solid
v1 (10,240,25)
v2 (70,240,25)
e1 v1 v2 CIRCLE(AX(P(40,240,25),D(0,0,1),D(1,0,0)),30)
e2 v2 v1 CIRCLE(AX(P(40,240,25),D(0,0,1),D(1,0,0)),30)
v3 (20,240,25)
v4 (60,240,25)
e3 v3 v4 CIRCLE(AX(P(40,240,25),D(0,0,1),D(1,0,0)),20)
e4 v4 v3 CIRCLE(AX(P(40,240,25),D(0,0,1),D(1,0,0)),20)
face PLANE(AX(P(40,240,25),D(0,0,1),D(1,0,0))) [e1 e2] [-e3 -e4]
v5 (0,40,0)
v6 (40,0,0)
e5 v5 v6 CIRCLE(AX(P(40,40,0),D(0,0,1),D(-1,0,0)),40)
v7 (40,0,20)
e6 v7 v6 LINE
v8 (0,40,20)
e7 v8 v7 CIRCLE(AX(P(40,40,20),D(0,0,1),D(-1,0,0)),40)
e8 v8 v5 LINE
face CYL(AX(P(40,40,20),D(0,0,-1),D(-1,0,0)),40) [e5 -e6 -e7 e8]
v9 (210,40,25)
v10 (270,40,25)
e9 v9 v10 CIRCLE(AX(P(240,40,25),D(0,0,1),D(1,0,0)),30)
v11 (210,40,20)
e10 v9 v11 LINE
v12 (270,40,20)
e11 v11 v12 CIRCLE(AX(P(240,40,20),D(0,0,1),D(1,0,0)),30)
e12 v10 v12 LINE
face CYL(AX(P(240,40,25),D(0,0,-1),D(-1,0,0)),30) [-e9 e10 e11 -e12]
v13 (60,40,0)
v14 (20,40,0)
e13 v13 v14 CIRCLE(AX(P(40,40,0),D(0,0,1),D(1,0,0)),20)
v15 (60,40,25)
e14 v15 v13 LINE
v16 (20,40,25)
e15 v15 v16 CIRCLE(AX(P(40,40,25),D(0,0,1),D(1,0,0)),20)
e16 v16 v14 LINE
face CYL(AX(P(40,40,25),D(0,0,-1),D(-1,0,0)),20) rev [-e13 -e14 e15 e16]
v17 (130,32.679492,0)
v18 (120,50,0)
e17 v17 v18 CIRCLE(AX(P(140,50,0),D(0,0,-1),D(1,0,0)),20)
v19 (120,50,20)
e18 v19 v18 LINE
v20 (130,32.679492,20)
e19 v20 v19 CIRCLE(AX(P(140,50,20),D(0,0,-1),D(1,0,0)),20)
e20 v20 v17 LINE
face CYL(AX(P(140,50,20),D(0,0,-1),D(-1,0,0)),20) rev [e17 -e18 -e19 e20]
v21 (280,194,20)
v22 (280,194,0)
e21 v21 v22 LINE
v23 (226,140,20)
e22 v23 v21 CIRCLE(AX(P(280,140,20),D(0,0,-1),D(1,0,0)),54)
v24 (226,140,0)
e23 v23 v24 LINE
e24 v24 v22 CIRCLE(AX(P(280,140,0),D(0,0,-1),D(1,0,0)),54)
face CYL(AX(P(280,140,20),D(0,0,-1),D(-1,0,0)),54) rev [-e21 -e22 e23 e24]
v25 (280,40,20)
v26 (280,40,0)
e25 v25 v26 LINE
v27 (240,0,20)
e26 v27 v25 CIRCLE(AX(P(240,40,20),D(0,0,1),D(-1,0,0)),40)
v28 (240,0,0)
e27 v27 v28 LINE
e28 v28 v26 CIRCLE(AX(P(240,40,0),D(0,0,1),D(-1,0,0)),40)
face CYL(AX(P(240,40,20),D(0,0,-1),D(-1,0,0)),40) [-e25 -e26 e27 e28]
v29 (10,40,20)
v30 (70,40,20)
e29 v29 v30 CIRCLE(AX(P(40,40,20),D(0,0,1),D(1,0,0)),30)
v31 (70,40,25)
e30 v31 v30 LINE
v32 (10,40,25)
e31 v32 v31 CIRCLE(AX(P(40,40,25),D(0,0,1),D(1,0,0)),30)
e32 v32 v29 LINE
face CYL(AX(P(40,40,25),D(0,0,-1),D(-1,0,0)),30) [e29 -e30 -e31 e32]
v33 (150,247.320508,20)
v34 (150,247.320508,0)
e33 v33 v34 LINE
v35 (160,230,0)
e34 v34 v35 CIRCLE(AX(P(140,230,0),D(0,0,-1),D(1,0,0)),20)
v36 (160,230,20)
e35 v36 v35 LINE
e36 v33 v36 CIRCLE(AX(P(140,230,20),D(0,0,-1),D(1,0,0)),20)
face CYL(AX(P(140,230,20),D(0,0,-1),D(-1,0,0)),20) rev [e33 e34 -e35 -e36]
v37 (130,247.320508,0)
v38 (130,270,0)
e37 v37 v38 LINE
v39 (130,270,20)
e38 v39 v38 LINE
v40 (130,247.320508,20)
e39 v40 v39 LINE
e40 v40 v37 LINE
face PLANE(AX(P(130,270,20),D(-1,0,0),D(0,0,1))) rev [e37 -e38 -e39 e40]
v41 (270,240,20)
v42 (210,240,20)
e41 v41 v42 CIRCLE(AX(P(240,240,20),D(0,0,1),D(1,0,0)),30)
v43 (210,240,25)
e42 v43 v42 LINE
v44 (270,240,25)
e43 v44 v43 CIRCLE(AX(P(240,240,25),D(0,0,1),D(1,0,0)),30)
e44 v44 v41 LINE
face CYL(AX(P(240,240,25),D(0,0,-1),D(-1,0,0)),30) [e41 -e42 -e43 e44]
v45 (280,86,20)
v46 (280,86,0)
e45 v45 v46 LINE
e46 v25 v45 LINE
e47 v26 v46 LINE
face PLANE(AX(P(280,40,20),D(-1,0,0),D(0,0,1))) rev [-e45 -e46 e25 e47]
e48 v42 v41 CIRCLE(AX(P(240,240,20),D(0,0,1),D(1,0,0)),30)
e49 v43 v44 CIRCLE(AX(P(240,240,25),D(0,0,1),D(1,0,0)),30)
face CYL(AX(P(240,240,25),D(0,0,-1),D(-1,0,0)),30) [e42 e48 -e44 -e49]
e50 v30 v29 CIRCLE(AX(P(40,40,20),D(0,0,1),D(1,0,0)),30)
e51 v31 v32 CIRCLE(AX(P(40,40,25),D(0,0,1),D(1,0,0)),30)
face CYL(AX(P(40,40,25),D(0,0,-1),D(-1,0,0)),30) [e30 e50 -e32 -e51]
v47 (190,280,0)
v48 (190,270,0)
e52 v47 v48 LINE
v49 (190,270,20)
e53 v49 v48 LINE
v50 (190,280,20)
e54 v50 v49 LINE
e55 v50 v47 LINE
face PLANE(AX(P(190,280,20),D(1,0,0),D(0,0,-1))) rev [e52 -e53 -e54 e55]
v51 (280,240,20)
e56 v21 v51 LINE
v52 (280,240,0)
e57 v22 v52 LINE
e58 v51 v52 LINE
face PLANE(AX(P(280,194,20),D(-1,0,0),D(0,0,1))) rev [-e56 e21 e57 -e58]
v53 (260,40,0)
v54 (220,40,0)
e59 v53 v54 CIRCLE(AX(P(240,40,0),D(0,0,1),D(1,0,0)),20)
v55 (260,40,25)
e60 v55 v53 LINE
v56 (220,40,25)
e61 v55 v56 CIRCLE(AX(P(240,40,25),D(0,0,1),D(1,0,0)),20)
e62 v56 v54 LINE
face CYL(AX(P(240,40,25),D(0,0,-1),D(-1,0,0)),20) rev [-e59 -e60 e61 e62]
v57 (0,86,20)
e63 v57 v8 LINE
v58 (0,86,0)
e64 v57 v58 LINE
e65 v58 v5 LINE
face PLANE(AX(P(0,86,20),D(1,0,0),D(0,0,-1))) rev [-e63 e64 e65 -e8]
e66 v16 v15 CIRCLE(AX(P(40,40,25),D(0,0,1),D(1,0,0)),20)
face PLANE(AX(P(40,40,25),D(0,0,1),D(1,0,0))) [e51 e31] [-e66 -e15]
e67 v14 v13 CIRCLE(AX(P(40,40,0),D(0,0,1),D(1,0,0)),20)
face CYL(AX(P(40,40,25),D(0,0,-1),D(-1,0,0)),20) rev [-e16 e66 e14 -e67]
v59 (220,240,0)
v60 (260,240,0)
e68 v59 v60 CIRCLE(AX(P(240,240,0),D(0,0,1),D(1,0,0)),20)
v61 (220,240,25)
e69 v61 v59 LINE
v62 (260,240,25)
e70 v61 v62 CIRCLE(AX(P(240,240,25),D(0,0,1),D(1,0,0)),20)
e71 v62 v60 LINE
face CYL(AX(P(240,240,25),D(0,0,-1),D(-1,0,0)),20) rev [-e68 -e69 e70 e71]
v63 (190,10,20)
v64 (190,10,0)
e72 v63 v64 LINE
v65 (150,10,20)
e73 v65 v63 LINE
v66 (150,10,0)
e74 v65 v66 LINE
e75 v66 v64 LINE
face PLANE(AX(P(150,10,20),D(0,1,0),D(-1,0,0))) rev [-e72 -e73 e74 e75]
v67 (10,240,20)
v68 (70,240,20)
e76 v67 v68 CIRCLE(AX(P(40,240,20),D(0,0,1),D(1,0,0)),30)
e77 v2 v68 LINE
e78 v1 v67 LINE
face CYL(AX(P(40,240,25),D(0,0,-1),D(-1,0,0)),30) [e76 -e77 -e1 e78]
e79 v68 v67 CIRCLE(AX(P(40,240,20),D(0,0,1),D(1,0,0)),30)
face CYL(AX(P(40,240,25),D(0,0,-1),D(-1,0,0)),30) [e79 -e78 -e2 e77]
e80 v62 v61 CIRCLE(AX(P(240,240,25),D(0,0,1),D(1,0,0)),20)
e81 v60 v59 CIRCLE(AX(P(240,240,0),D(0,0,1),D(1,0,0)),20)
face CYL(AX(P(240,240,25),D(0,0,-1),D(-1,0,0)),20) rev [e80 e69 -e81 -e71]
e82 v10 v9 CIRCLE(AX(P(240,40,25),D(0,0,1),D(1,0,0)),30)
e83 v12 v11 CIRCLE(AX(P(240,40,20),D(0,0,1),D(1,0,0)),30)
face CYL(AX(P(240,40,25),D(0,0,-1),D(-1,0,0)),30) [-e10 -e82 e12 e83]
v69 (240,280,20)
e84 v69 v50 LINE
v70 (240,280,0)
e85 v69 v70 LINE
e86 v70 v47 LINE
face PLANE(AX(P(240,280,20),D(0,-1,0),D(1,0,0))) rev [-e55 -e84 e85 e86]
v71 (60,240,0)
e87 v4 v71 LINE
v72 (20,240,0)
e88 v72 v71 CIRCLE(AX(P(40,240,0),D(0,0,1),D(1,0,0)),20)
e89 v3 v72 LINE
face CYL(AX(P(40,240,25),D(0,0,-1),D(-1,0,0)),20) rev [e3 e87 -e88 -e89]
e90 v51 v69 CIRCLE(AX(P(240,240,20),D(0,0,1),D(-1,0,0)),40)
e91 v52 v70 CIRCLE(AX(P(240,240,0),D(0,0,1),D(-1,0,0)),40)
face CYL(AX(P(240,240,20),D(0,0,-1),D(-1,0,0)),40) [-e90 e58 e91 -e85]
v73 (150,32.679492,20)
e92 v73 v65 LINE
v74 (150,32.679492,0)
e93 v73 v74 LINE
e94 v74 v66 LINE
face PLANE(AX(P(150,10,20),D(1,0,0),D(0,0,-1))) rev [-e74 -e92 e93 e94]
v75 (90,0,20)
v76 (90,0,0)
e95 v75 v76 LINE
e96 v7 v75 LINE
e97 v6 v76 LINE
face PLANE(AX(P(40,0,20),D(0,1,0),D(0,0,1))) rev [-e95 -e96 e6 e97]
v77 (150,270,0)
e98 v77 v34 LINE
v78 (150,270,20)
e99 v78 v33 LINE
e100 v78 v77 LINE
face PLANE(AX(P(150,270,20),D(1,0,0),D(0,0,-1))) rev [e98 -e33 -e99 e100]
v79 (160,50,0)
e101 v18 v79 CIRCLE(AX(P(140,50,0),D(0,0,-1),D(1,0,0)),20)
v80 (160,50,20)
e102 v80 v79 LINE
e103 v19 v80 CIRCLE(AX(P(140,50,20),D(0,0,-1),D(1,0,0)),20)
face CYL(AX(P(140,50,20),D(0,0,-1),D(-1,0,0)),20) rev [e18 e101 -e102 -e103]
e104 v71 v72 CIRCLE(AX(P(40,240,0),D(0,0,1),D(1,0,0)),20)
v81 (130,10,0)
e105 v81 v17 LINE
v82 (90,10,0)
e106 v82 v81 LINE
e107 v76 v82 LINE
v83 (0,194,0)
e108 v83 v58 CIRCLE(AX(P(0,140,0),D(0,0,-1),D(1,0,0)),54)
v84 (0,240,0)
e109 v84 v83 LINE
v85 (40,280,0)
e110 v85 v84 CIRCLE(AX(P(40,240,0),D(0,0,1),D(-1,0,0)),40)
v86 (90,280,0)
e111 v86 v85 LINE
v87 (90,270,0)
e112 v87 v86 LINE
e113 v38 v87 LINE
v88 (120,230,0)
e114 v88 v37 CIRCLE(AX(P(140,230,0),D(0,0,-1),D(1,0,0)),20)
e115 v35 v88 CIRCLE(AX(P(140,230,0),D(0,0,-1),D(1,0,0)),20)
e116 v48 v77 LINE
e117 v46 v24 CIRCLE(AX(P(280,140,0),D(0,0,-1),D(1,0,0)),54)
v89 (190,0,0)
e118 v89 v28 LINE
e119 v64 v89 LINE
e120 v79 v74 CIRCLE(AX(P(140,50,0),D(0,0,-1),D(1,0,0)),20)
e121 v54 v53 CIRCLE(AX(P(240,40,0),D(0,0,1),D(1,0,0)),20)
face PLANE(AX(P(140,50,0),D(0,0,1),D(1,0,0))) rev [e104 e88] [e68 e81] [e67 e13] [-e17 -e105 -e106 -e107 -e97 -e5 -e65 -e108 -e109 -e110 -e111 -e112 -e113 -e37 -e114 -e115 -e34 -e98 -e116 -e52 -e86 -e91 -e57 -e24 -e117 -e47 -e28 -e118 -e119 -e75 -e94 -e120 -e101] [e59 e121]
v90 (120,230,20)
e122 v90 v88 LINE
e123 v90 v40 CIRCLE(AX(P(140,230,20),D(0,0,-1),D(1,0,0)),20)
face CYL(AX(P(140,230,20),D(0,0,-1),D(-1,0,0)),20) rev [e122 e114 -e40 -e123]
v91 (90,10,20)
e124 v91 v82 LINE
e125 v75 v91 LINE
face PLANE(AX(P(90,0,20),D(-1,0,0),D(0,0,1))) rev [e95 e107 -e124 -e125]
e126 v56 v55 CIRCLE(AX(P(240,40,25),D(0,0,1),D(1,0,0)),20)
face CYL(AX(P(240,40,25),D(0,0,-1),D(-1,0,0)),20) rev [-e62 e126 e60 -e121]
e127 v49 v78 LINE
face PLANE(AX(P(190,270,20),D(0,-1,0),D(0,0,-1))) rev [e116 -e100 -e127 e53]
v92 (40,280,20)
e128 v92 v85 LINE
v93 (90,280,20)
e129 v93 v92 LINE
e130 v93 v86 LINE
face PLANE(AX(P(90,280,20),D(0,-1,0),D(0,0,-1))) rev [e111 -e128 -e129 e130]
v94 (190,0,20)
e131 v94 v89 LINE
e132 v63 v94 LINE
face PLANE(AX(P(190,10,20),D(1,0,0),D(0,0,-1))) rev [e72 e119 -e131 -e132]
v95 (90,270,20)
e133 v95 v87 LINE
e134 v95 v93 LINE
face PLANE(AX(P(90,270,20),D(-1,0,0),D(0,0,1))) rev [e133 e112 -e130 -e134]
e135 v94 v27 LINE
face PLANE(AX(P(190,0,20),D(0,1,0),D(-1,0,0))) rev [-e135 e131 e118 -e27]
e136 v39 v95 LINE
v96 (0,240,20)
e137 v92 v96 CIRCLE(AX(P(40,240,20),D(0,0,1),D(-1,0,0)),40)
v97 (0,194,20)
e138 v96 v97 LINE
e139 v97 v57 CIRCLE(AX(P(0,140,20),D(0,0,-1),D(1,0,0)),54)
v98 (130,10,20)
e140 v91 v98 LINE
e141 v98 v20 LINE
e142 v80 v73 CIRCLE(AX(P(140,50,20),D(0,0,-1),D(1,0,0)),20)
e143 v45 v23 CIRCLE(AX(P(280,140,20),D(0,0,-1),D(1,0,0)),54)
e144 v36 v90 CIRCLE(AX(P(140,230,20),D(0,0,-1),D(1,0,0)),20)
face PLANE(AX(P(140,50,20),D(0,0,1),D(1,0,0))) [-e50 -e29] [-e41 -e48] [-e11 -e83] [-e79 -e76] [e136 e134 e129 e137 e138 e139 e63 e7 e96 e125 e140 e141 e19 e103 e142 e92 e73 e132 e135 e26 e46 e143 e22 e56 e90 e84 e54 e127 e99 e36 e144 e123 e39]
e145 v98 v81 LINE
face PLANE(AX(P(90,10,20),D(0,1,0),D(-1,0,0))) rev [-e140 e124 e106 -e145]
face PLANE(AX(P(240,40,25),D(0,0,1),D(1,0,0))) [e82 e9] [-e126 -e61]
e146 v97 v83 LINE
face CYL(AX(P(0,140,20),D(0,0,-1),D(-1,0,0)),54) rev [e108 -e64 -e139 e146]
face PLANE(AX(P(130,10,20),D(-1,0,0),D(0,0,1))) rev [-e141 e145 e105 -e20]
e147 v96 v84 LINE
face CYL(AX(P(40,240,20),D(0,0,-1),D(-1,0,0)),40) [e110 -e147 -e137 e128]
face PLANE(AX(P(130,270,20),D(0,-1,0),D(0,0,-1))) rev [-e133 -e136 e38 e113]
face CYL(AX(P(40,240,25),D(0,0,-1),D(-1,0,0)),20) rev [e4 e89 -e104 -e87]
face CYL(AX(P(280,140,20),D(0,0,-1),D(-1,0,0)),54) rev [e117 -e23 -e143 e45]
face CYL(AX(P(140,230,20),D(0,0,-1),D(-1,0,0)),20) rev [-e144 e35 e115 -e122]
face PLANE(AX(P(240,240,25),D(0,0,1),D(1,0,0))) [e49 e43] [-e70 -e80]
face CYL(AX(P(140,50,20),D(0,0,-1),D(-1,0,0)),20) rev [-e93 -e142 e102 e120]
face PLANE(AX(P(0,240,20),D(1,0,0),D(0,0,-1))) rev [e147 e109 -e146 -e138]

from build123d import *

# Parameters (mm, degrees)
BASE_PLATE_20MM_DEPTH          = 20
MOUNTING_BOSS_RINGS_SKETCH_R   = 30
MOUNTING_BOSS_RINGS_SKETCH_R_2 = 20
MOUNTING_BOSSES_4X_60_DEPTH    = 5
TOP_NOTCH_SKETCH_R             = 20
TOP_NOTCH_CUT_DEPTH            = 397.484552032


with BuildPart() as part:
    # Plate Profile Sketch → Base Plate 20mm (new body)
    with BuildSketch(Plane.XY):
        with BuildLine():
            Line((40, 0), (90, 0))
            Line((90, 0), (90, 10))
            Line((90, 10), (130, 10))
            Line((130, 10), (130, 32.679491924))
            ThreePointArc((130, 32.679491924), (140, 70), (150, 32.679491924))
            Line((150, 32.679491924), (150, 10))
            Line((150, 10), (190, 10))
            Line((190, 10), (190, 0))
            Line((190, 0), (240, 0))
            ThreePointArc((240, 0), (268.284271247, 11.715728753), (280, 40))
            Line((280, 40), (280, 86))
            ThreePointArc((280, 86), (226, 140), (280, 194))
            Line((280, 194), (280, 240))
            ThreePointArc((280, 240), (268.284271247, 268.284271247), (240, 280))
            Line((240, 280), (190, 280))
            Line((190, 280), (190, 270))
            Line((190, 270), (150, 270))
            Line((150, 270), (150, 247.320508076))
            ThreePointArc((150, 247.320508076), (140, 210), (130, 247.320508076))
            Line((130, 247.320508076), (130, 270))
            Line((130, 270), (90, 270))
            Line((90, 270), (90, 280))
            Line((90, 280), (40, 280))
            ThreePointArc((40, 280), (11.715728753, 268.284271247), (0, 240))
            Line((0, 240), (0, 194))
            ThreePointArc((0, 194), (54, 140), (0, 86))
            Line((0, 86), (0, 40))
            ThreePointArc((0, 40), (11.715728753, 11.715728753), (40, 0))
        make_face()
    extrude(amount=BASE_PLATE_20MM_DEPTH)

    # Mounting Boss Rings Sketch → Mounting Bosses 4xØ60 (add)
    # profile 1 of 4: a face of its own
    with BuildSketch(Plane.XY.offset(20)):
        with Locations((240, 240)):
            Circle(MOUNTING_BOSS_RINGS_SKETCH_R)
        with Locations((240, 240)):
            Circle(MOUNTING_BOSS_RINGS_SKETCH_R_2, mode=Mode.SUBTRACT)
    # profile 2 of 4: a face of its own
    with BuildSketch(Plane.XY.offset(20)):
        with Locations((40, 240)):
            Circle(MOUNTING_BOSS_RINGS_SKETCH_R)
        with Locations((40, 240)):
            Circle(MOUNTING_BOSS_RINGS_SKETCH_R_2, mode=Mode.SUBTRACT)
    # profile 3 of 4: a face of its own
    with BuildSketch(Plane.XY.offset(20)):
        with Locations((240, 40)):
            Circle(MOUNTING_BOSS_RINGS_SKETCH_R)
        with Locations((240, 40)):
            Circle(MOUNTING_BOSS_RINGS_SKETCH_R_2, mode=Mode.SUBTRACT)
    # profile 4 of 4: a face of its own
    with BuildSketch(Plane.XY.offset(20)):
        with Locations((40, 40)):
            Circle(MOUNTING_BOSS_RINGS_SKETCH_R)
        with Locations((40, 40)):
            Circle(MOUNTING_BOSS_RINGS_SKETCH_R_2, mode=Mode.SUBTRACT)
    extrude(amount=MOUNTING_BOSSES_4X_60_DEPTH)

    # Top Notch Sketch → Top Notch Cut (cut, through all)
    with BuildSketch(Plane.XY.offset(20)):
        with Locations((40, 240)):
            Circle(TOP_NOTCH_SKETCH_R)
        with Locations((240, 240)):
            Circle(TOP_NOTCH_SKETCH_R)
        with Locations((240, 40)):
            Circle(TOP_NOTCH_SKETCH_R)
        with Locations((40, 40)):
            Circle(TOP_NOTCH_SKETCH_R)
    extrude(amount=-TOP_NOTCH_CUT_DEPTH, mode=Mode.SUBTRACT)


solid = part.part
